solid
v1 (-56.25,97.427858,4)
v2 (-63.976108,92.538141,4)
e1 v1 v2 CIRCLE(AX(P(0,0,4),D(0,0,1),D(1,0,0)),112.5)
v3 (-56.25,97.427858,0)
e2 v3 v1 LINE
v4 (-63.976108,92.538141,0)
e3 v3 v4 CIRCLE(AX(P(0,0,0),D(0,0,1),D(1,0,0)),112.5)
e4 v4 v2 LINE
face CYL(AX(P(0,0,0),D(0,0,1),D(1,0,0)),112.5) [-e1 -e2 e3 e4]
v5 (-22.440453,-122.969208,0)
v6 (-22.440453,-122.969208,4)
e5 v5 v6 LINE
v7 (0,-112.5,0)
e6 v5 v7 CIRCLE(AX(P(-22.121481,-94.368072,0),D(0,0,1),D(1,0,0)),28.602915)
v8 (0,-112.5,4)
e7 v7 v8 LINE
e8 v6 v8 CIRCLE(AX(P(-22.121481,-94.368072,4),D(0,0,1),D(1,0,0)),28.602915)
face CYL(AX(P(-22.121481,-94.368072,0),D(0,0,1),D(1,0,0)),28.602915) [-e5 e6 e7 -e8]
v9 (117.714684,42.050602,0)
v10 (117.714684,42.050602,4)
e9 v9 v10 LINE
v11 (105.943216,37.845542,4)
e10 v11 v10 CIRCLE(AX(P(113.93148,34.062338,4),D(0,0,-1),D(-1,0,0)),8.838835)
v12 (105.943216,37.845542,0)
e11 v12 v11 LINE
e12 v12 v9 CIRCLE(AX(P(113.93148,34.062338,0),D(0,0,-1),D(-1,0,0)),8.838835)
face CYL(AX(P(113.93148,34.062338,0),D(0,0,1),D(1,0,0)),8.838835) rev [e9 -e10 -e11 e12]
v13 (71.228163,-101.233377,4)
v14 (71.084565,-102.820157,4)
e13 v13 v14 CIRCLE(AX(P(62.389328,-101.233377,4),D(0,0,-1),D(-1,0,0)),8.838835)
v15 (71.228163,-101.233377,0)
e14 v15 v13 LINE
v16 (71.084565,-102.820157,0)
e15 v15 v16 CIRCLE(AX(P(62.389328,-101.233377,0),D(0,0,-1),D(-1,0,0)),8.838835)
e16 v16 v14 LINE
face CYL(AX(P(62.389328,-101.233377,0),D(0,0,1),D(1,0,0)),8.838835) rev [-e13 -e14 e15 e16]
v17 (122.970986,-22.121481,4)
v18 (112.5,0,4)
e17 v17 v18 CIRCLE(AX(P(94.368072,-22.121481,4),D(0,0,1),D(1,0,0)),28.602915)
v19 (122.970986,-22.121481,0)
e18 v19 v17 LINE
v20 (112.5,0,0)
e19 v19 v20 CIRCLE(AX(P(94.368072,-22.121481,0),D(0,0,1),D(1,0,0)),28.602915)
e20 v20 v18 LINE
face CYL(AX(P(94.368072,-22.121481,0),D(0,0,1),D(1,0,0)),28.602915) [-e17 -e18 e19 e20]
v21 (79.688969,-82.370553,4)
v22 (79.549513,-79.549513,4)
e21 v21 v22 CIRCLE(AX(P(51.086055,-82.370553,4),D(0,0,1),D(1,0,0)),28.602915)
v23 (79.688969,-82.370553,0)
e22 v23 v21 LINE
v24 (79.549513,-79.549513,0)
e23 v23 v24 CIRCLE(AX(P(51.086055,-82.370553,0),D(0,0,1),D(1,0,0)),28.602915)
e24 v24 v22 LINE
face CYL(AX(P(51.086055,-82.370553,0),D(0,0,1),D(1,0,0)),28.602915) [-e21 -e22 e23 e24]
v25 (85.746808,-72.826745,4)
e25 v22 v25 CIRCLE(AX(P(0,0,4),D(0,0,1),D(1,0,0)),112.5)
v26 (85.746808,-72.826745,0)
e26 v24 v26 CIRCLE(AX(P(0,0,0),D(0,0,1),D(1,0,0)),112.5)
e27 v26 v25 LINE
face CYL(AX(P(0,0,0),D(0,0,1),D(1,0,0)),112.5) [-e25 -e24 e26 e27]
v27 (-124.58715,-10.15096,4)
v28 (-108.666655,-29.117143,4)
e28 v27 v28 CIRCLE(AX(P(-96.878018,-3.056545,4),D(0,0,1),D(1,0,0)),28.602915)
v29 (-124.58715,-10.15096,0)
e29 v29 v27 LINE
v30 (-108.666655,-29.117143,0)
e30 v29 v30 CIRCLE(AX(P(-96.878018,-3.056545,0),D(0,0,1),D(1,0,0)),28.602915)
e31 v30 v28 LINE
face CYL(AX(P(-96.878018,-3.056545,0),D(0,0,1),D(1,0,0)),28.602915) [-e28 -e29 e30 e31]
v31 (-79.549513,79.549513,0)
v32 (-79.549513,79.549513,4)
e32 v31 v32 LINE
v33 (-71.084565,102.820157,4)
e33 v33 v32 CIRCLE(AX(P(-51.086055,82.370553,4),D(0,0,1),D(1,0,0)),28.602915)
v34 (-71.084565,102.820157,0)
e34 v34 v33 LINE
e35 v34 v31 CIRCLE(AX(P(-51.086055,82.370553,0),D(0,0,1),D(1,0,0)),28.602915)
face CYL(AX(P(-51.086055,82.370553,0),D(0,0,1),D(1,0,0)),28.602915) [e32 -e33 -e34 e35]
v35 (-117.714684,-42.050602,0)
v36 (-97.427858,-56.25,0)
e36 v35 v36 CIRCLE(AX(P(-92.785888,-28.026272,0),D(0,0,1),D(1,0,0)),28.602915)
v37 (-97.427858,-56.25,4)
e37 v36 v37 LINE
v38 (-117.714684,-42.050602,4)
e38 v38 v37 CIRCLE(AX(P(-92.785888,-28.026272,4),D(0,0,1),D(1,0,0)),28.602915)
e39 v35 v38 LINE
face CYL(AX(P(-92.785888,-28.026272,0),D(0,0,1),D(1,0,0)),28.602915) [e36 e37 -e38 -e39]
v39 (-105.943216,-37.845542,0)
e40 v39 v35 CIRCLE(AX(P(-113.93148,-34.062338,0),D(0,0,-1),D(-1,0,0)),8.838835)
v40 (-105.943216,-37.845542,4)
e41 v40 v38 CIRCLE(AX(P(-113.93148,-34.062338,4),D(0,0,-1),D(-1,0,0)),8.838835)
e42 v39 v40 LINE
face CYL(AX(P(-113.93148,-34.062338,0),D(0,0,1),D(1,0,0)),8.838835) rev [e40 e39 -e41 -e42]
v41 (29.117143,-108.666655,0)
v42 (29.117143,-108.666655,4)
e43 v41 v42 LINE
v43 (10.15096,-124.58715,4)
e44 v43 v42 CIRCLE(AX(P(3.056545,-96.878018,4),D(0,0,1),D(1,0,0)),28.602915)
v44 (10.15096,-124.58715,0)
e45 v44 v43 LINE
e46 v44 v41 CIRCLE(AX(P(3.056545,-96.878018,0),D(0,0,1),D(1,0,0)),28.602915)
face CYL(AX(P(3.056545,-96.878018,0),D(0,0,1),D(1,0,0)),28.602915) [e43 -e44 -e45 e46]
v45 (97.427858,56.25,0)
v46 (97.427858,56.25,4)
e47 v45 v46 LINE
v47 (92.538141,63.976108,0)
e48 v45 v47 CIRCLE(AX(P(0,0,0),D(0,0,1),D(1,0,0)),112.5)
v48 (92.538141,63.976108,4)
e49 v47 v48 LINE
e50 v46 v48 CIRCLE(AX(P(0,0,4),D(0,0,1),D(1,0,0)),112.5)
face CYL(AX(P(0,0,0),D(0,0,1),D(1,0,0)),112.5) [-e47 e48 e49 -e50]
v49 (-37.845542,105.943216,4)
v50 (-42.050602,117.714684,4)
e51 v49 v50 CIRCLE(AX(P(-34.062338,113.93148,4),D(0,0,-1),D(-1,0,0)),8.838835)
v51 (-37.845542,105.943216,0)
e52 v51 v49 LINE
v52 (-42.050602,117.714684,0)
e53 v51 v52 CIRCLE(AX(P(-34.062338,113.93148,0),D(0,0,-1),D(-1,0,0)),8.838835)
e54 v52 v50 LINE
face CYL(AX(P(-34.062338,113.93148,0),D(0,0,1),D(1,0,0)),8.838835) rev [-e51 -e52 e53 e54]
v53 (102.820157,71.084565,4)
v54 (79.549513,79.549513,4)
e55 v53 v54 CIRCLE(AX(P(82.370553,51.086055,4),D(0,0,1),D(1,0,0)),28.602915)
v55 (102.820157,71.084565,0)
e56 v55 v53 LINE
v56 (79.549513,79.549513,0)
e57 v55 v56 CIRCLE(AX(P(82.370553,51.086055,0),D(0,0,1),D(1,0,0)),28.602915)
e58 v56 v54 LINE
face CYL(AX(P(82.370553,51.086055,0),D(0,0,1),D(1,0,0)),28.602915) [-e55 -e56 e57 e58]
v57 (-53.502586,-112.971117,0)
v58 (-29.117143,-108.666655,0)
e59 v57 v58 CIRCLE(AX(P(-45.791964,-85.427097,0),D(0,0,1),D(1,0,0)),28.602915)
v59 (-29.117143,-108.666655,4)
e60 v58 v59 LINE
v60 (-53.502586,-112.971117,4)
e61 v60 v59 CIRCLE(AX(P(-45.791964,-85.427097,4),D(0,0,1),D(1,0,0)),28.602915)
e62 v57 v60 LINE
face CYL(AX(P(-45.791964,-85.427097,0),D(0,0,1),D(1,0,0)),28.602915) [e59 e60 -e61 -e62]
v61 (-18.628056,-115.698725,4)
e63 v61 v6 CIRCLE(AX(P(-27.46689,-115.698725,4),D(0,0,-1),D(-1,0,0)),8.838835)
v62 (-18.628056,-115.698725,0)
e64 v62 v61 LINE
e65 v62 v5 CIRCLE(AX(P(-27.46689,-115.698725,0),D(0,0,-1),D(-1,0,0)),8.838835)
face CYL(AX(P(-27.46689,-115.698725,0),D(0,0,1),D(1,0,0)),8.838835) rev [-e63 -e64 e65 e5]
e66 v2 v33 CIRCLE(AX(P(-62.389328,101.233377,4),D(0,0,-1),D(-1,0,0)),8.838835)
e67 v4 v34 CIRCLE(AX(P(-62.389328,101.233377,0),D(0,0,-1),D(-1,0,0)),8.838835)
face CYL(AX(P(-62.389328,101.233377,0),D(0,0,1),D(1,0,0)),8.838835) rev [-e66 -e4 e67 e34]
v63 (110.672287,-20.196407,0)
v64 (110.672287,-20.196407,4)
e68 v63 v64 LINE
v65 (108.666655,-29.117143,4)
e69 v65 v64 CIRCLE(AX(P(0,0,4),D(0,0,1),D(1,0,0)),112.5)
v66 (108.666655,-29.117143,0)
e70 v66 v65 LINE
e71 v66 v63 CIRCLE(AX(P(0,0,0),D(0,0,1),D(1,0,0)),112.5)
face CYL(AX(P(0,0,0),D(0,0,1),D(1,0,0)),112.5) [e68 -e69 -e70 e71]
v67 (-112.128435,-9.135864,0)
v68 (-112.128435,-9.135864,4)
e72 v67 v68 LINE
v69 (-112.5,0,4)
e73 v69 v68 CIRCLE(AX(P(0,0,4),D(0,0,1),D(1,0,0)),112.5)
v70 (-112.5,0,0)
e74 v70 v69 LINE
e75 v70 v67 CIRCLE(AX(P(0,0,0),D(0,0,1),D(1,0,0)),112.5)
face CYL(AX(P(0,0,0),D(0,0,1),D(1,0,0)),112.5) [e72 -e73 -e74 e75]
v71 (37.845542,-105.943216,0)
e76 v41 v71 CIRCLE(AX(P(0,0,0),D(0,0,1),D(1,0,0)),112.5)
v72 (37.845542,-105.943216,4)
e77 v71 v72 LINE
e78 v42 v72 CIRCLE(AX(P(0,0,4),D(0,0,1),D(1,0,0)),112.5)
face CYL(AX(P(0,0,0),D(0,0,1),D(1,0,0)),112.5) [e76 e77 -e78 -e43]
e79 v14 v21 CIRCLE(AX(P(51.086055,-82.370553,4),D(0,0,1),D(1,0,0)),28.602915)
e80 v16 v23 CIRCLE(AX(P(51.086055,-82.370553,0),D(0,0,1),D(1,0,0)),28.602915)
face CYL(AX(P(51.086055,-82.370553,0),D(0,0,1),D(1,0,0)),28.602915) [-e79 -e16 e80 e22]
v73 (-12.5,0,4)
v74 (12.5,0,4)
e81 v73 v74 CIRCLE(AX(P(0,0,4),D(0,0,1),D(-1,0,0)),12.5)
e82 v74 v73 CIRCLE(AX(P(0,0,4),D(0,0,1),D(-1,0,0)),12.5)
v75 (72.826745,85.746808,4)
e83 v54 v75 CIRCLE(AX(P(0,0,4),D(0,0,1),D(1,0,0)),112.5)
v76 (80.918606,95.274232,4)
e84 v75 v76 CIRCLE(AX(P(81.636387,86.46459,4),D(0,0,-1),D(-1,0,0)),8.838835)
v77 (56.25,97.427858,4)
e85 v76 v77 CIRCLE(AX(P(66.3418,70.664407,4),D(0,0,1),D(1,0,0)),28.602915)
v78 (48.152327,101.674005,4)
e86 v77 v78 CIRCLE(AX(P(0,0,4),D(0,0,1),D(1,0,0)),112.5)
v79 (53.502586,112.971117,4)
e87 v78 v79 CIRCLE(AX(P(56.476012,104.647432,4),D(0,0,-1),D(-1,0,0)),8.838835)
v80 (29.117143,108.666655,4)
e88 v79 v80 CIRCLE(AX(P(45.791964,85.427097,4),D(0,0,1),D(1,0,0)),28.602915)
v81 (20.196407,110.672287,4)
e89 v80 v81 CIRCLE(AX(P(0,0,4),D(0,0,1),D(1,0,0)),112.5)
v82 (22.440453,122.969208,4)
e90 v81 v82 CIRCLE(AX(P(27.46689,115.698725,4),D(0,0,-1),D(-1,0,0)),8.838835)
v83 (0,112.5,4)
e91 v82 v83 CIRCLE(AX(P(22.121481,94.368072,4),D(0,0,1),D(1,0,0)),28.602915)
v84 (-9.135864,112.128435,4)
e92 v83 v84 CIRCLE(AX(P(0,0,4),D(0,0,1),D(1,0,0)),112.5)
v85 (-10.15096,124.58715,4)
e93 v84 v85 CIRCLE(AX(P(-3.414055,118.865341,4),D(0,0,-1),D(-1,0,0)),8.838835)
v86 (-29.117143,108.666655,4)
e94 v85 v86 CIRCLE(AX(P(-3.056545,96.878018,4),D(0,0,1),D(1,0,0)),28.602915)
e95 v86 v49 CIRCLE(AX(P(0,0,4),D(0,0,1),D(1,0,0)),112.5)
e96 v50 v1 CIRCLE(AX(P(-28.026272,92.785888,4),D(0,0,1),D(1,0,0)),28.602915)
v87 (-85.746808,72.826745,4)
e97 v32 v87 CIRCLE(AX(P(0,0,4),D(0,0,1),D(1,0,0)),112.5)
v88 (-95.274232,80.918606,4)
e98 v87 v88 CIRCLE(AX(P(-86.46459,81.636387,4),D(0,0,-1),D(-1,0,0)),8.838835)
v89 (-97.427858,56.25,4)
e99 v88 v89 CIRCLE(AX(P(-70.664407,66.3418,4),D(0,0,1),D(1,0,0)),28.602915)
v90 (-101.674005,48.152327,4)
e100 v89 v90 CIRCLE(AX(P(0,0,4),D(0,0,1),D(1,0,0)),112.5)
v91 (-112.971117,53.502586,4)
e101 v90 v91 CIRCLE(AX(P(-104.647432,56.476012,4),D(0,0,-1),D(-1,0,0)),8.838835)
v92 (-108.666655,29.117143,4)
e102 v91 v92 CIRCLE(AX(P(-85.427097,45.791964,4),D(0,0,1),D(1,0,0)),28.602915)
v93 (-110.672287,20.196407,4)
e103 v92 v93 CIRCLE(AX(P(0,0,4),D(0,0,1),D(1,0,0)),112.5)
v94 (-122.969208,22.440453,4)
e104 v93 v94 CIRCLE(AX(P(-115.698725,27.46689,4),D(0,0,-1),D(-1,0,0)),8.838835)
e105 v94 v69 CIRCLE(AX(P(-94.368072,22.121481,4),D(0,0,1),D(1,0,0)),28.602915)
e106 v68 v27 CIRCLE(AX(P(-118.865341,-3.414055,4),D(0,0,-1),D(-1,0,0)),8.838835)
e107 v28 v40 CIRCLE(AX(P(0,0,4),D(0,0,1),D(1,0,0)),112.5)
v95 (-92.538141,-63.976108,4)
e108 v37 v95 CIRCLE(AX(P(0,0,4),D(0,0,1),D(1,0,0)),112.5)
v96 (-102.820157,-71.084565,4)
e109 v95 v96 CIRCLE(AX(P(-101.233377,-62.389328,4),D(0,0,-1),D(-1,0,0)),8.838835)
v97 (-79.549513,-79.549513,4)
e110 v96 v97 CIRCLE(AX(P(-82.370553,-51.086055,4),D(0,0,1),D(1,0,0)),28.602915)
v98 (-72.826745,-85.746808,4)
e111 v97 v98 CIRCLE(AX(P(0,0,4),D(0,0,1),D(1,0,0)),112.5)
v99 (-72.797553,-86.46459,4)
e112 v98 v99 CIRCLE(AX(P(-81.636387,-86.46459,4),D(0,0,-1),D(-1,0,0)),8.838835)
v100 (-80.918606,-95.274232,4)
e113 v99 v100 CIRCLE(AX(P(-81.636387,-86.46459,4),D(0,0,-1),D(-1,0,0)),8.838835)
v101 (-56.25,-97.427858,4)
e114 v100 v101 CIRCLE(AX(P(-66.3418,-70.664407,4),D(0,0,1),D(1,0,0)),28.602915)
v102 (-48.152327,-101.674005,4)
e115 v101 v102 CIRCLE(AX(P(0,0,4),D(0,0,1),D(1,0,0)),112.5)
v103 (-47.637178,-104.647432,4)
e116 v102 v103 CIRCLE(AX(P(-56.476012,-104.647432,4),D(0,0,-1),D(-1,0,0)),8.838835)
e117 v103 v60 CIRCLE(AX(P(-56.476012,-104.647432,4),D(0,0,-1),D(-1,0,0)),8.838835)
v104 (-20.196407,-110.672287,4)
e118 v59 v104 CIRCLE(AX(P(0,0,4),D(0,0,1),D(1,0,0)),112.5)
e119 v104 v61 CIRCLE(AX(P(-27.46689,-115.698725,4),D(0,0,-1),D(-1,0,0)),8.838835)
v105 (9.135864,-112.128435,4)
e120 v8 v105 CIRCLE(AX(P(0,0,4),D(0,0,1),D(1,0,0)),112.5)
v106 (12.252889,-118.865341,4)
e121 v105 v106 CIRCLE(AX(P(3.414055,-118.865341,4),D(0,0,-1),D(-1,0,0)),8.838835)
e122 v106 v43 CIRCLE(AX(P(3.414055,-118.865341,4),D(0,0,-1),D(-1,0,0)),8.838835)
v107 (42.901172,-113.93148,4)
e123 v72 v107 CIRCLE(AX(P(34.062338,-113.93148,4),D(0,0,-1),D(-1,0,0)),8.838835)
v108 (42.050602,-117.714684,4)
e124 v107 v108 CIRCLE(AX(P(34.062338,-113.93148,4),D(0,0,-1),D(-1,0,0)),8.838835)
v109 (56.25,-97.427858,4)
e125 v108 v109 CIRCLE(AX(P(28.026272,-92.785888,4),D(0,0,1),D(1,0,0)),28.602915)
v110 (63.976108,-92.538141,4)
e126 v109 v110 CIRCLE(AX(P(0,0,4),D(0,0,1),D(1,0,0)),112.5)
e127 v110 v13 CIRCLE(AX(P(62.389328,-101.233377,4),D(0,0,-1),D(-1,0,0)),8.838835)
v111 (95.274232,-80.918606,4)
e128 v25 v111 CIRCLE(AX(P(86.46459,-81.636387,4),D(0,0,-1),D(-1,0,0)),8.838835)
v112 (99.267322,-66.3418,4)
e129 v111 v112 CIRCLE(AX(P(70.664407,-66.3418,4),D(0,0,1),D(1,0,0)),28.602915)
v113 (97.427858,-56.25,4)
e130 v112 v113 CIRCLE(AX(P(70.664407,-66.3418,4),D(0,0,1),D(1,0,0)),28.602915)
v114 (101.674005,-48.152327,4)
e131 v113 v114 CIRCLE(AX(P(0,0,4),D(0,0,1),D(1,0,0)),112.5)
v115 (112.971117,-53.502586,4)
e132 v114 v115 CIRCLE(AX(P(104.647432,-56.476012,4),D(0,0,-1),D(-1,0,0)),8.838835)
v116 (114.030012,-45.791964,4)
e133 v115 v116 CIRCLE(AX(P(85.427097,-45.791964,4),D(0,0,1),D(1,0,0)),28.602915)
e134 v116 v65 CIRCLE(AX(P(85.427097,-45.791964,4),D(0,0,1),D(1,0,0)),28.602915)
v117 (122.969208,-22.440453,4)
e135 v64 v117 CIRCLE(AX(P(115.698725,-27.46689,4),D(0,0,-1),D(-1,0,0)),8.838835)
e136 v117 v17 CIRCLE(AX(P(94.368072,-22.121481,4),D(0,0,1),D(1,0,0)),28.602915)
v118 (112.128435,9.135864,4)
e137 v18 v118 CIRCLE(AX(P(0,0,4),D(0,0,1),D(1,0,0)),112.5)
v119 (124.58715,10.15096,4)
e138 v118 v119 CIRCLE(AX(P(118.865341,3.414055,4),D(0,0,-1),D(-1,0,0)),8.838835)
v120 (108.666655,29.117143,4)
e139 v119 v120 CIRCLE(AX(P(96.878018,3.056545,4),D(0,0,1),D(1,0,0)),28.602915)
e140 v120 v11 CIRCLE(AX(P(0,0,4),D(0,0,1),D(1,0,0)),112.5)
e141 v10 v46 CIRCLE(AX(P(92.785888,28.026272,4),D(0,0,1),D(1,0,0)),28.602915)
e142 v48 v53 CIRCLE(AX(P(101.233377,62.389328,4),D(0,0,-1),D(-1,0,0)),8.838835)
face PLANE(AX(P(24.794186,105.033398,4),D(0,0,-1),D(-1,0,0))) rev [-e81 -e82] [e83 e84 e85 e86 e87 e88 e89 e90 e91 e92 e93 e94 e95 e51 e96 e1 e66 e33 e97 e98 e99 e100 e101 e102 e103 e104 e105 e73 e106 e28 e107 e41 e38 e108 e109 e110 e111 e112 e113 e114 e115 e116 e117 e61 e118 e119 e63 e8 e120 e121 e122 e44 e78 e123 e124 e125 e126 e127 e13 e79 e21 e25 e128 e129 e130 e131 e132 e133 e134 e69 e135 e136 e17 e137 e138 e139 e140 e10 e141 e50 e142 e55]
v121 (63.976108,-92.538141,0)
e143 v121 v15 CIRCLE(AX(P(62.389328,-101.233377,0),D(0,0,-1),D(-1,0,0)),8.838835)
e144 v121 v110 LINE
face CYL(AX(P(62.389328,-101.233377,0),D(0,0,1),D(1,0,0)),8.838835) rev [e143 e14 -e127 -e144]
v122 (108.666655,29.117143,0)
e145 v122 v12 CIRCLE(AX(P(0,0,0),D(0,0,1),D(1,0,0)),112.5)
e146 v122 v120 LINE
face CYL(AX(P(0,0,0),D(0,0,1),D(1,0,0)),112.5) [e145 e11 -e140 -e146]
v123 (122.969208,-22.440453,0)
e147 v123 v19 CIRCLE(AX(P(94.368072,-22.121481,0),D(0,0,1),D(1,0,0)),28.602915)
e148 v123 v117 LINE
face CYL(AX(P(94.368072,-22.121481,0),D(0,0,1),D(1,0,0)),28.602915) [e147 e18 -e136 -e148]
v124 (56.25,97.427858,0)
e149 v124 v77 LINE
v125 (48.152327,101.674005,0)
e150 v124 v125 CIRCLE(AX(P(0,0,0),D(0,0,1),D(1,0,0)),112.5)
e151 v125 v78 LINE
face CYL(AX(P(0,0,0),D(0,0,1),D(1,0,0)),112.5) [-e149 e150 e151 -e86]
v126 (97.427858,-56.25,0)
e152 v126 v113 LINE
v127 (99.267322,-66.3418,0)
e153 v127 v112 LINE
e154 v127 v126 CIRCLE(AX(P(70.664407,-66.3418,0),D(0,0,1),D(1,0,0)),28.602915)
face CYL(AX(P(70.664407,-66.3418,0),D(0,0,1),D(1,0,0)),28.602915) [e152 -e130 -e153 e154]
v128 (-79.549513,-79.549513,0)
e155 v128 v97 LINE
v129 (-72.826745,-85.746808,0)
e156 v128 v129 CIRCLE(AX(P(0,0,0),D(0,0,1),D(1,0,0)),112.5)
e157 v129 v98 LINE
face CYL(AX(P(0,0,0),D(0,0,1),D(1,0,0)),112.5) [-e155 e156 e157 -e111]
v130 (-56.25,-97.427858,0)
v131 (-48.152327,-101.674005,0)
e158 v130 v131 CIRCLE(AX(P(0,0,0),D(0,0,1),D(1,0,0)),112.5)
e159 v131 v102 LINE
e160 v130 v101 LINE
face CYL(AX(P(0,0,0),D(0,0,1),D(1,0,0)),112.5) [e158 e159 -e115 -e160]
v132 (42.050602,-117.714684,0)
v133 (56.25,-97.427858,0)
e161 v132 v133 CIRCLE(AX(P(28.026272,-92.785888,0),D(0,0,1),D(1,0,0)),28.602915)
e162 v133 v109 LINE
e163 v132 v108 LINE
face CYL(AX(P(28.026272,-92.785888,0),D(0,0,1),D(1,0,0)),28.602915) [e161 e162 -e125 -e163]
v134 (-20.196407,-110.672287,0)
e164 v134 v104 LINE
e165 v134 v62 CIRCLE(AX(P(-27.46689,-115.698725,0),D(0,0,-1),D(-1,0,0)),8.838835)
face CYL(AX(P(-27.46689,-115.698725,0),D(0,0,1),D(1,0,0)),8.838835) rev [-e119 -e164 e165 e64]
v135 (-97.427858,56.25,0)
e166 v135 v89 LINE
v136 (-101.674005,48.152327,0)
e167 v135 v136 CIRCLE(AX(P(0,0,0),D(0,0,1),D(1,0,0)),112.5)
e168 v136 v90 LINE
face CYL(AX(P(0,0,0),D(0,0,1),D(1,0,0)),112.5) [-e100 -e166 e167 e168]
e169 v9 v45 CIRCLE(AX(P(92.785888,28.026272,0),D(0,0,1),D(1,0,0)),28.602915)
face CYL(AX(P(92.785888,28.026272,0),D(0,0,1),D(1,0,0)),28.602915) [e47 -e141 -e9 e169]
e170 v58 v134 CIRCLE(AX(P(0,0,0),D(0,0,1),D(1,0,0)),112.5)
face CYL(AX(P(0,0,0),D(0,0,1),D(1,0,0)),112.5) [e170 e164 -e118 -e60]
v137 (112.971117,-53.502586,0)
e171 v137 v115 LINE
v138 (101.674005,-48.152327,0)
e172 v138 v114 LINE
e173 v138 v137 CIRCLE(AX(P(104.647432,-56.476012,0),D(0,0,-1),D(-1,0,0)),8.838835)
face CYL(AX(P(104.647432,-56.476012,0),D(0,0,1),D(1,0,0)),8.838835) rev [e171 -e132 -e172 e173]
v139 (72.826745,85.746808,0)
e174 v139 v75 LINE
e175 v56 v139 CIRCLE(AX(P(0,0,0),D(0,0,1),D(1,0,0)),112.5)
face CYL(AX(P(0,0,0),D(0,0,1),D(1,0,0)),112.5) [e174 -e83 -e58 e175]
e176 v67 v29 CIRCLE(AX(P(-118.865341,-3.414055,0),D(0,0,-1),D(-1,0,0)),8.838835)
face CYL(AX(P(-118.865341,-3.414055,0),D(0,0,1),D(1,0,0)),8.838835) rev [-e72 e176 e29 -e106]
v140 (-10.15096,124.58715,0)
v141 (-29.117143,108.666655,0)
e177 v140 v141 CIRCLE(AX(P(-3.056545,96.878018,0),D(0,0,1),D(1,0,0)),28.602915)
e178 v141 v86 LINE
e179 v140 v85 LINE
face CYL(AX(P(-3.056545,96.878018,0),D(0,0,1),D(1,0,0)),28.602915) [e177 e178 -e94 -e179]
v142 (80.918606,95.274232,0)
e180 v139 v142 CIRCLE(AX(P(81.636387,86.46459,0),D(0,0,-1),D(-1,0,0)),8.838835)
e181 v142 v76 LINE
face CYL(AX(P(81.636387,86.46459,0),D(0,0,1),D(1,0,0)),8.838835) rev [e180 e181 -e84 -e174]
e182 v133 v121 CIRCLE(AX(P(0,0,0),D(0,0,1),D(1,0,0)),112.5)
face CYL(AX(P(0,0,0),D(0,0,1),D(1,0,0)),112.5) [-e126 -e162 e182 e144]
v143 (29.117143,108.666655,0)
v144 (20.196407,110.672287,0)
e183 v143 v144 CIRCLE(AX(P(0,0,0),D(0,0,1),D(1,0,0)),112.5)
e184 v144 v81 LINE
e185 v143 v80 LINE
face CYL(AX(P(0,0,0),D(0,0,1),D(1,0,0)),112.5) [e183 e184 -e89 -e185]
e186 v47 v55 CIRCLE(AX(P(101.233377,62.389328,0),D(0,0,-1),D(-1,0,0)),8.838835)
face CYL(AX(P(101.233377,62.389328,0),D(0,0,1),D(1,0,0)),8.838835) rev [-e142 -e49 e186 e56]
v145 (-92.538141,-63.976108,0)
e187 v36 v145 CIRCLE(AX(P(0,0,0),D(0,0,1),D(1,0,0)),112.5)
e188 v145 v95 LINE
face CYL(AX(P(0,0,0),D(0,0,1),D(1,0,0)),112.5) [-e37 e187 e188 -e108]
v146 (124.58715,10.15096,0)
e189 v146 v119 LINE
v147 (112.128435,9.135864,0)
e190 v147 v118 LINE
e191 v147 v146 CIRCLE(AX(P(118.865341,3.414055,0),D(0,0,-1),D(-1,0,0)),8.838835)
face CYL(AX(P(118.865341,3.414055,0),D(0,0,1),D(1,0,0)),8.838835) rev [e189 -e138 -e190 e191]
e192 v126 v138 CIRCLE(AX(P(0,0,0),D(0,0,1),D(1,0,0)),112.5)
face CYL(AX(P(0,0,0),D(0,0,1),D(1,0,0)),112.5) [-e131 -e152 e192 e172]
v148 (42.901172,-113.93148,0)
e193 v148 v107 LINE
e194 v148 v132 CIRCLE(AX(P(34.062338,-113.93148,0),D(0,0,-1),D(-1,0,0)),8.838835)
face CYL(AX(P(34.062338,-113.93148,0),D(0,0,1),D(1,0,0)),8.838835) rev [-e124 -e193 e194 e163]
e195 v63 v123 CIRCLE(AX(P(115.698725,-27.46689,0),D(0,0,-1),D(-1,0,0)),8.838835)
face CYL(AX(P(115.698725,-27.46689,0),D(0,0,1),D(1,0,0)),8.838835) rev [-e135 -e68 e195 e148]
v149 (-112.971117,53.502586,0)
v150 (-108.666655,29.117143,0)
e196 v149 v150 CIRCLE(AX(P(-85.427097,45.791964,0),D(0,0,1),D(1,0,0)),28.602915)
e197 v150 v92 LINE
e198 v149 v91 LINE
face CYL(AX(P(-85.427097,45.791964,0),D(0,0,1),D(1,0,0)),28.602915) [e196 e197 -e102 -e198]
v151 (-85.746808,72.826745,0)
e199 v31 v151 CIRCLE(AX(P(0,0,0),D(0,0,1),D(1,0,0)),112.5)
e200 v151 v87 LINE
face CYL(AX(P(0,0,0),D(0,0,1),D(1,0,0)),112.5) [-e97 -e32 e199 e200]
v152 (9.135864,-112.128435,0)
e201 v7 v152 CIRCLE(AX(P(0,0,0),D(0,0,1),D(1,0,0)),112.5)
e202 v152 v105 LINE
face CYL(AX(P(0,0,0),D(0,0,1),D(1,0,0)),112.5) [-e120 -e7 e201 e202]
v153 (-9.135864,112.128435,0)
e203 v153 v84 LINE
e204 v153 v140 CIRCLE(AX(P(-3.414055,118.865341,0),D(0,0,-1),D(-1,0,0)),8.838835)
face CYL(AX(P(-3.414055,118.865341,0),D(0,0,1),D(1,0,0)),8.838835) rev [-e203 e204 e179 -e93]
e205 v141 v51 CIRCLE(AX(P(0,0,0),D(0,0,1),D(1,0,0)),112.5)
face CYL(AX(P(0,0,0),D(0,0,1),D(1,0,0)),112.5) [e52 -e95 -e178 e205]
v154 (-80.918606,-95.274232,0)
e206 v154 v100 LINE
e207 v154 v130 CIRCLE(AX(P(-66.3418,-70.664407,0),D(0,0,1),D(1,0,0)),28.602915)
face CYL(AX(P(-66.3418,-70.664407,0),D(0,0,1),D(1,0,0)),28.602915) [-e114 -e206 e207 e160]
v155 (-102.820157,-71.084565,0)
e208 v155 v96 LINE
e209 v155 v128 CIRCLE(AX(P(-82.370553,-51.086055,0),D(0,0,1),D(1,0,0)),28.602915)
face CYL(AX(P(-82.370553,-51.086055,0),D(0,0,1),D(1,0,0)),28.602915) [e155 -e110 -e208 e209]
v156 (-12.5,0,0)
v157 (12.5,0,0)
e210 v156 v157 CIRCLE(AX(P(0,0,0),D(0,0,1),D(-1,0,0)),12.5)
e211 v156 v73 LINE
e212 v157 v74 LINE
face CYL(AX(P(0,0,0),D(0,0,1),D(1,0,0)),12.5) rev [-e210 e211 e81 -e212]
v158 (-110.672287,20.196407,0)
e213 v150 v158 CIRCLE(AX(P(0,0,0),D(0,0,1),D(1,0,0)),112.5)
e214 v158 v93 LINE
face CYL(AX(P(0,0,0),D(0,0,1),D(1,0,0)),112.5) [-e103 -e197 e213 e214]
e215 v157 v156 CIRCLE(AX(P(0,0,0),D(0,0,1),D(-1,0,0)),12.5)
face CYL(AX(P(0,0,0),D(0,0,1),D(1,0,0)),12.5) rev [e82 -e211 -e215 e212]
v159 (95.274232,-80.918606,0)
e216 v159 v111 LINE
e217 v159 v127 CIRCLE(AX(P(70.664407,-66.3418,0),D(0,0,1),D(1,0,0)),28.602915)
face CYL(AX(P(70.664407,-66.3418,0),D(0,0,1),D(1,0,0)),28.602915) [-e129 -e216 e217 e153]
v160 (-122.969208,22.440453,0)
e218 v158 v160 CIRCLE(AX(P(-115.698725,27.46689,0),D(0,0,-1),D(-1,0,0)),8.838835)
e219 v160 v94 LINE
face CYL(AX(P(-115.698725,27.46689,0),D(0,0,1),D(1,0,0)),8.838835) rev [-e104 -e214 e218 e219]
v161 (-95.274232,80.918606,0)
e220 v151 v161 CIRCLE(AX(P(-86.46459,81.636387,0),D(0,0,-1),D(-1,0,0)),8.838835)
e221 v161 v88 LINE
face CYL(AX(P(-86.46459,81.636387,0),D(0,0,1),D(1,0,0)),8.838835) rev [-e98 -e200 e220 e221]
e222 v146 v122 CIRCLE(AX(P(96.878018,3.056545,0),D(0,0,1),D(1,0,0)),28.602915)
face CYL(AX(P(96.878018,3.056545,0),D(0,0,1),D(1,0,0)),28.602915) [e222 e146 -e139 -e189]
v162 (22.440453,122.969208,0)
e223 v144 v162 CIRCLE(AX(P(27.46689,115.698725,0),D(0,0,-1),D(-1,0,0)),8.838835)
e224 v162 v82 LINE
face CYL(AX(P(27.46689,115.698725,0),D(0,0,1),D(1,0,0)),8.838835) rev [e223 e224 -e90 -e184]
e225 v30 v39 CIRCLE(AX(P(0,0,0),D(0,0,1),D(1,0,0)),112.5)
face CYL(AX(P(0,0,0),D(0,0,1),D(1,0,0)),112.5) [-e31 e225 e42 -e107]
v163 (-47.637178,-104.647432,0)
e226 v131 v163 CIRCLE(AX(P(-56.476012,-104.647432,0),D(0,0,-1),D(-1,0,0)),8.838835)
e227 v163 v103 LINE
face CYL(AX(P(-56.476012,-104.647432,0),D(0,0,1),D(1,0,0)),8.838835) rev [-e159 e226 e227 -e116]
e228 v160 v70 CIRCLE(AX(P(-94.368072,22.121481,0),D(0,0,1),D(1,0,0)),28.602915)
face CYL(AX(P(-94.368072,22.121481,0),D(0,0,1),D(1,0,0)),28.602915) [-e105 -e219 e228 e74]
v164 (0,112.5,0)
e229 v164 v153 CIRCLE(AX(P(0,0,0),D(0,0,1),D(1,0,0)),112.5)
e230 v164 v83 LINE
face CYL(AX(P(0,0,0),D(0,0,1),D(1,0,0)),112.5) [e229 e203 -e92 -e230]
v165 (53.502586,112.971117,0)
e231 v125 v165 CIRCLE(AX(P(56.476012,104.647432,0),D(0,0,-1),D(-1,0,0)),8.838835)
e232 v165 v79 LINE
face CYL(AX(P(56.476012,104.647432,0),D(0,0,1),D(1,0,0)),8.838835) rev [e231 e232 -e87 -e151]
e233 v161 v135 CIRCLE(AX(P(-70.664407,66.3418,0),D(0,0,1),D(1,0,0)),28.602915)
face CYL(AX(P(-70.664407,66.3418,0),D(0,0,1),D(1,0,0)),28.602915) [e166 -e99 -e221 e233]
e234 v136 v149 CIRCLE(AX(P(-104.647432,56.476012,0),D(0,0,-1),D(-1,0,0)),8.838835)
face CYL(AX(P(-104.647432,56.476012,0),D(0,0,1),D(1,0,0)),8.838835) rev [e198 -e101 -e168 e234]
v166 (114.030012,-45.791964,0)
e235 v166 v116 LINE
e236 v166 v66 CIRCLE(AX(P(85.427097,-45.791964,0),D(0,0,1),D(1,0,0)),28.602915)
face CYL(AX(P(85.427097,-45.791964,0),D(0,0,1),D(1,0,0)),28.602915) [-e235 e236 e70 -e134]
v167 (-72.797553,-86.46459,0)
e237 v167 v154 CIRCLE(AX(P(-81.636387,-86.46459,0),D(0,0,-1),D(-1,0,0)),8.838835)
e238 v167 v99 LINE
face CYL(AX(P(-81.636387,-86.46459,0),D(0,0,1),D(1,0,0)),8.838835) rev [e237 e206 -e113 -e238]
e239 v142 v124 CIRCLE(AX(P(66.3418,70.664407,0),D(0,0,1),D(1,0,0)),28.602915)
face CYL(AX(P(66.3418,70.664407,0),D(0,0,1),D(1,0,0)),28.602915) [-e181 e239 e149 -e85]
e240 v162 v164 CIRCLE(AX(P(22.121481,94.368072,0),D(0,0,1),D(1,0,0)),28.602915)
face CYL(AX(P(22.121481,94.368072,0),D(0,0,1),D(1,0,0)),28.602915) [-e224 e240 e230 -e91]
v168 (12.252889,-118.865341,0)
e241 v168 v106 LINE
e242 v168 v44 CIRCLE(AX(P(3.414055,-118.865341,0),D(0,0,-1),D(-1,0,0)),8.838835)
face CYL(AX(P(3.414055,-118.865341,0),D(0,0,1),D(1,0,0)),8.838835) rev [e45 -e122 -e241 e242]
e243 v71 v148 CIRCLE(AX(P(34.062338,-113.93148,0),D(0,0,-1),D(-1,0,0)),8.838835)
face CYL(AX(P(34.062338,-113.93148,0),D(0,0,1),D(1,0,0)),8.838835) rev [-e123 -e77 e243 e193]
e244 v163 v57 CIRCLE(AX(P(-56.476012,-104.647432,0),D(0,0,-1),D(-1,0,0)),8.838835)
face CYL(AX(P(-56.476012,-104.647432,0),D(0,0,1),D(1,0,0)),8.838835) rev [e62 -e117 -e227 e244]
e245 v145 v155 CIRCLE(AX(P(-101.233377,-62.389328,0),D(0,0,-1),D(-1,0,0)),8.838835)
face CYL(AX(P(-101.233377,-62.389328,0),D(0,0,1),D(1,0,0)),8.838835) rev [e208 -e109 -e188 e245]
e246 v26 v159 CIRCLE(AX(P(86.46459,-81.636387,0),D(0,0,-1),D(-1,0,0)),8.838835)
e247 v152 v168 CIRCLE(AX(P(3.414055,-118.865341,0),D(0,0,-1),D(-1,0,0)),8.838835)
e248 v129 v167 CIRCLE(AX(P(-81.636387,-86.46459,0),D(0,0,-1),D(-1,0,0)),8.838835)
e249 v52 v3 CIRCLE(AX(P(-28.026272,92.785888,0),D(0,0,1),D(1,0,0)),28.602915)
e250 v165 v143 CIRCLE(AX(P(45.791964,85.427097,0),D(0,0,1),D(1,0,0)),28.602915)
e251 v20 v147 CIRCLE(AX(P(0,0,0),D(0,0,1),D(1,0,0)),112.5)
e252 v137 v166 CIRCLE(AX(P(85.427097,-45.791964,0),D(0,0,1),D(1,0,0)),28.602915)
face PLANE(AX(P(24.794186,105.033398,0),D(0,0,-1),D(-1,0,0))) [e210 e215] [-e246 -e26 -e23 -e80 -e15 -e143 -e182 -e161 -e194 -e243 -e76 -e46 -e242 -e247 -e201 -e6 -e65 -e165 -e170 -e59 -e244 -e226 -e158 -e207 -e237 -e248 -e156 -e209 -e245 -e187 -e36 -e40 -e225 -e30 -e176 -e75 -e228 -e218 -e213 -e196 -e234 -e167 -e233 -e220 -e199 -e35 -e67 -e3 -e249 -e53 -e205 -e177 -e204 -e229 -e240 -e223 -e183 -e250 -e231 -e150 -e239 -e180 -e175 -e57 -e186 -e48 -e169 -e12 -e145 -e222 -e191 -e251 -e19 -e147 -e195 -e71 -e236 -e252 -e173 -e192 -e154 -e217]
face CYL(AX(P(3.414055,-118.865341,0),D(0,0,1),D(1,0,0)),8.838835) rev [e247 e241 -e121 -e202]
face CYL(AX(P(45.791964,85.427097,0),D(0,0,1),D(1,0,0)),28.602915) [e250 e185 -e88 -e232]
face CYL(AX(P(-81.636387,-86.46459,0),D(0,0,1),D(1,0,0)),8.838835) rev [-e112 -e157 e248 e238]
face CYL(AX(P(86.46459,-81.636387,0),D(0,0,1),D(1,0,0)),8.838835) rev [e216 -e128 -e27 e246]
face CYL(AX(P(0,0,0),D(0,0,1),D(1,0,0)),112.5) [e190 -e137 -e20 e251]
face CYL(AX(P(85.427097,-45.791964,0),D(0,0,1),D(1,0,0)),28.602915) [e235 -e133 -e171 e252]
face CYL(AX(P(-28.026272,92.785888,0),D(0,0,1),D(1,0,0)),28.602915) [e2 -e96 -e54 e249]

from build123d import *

# Parameters (mm, degrees)
SKETCH1_R           = 12.5
BOSS_EXTRUDE1_DEPTH = 4


with BuildPart() as part:
    # Sketch1 → Boss-Extrude1 (new body)
    with BuildSketch(Plane.XY.offset(4)):
        with BuildLine():
            ThreePointArc((22.440452668, 122.96920787), (10.028572641, 120.288880116), (0, 112.5))
            ThreePointArc((0, 112.5), (-4.571708495, 112.407070425), (-9.135864155, 112.128435226))
            ThreePointArc((-9.135864155, 112.128435226), (-12.223696531, 118.147559469), (-10.150960173, 124.587150251))
            ThreePointArc((-10.150960173, 124.587150251), (-21.446195774, 118.785721514), (-29.117142574, 108.666655458))
            ThreePointArc((-29.117142574, 108.666655458), (-33.509021935, 107.393647153), (-37.845541667, 105.943215809))
            ThreePointArc((-37.845541667, 105.943215809), (-42.386022695, 110.958053541), (-42.050601852, 117.714684232))
            ThreePointArc((-42.050601852, 117.714684232), (-51.459441387, 109.187512293), (-56.25, 97.427857926))
            ThreePointArc((-56.25, 97.427857926), (-60.162750907, 95.061524305), (-63.976108057, 92.538141314))
            ThreePointArc((-63.976108057, 92.538141314), (-69.659811458, 96.20693963), (-71.084564508, 102.820157016))
            ThreePointArc((-71.084564508, 102.820157016), (-77.965811111, 92.148354551), (-79.549512883, 79.549512883))
            ThreePointArc((-79.549512883, 79.549512883), (-82.716487829, 76.251115672), (-85.746808408, 72.826745416))
            ThreePointArc((-85.746808408, 72.826745416), (-92.186399189, 74.899481774), (-95.274231565, 80.918606017))
            ThreePointArc((-95.274231565, 80.918606017), (-99.158939653, 68.829438728), (-97.427857926, 56.25))
            ThreePointArc((-97.427857926, 56.25), (-99.6332328, 52.244319517), (-101.67400547, 48.152327169))
            ThreePointArc((-101.67400547, 48.152327169), (-108.430636161, 48.487748011), (-112.971117188, 53.502585743))
            ThreePointArc((-112.971117188, 53.502585743), (-113.594550325, 40.819910403), (-108.666655458, 29.117142574))
            ThreePointArc((-108.666655458, 29.117142574), (-109.760137608, 24.677159325), (-110.672287083, 20.196407401))
            ThreePointArc((-110.672287083, 20.196407401), (-117.285504468, 18.771654352), (-122.96920787, 22.440452668))
            ThreePointArc((-122.96920787, 22.440452668), (-120.288880116, 10.028572641), (-112.5, 0))
            ThreePointArc((-112.5, 0), (-112.407070425, -4.571708495), (-112.128435226, -9.135864155))
            ThreePointArc((-112.128435226, -9.135864155), (-118.147559469, -12.223696531), (-124.587150251, -10.150960173))
            ThreePointArc((-124.587150251, -10.150960173), (-118.785721514, -21.446195774), (-108.666655458, -29.117142574))
            ThreePointArc((-108.666655458, -29.117142574), (-107.393647153, -33.509021935), (-105.943215809, -37.845541667))
            ThreePointArc((-105.943215809, -37.845541667), (-110.958053541, -42.386022695), (-117.714684232, -42.050601852))
            ThreePointArc((-117.714684232, -42.050601852), (-109.187512293, -51.459441387), (-97.427857926, -56.25))
            ThreePointArc((-97.427857926, -56.25), (-95.061524305, -60.162750907), (-92.538141314, -63.976108057))
            ThreePointArc((-92.538141314, -63.976108057), (-96.20693963, -69.659811458), (-102.820157016, -71.084564508))
            ThreePointArc((-102.820157016, -71.084564508), (-92.148354551, -77.965811111), (-79.549512883, -79.549512883))
            ThreePointArc((-79.549512883, -79.549512883), (-76.251115672, -82.716487829), (-72.826745416, -85.746808408))
            ThreePointArc((-72.826745416, -85.746808408), (-74.899481774, -92.186399189), (-80.918606017, -95.274231565))
            ThreePointArc((-80.918606017, -95.274231565), (-68.829438728, -99.158939653), (-56.25, -97.427857926))
            ThreePointArc((-56.25, -97.427857926), (-52.244319517, -99.6332328), (-48.152327169, -101.67400547))
            ThreePointArc((-48.152327169, -101.67400547), (-48.487748011, -108.430636161), (-53.502585743, -112.971117188))
            ThreePointArc((-53.502585743, -112.971117188), (-40.819910403, -113.594550325), (-29.117142574, -108.666655458))
            ThreePointArc((-29.117142574, -108.666655458), (-24.677159325, -109.760137608), (-20.196407401, -110.672287083))
            ThreePointArc((-20.196407401, -110.672287083), (-18.771654352, -117.285504468), (-22.440452668, -122.96920787))
            ThreePointArc((-22.440452668, -122.96920787), (-10.028572641, -120.288880116), (0, -112.5))
            ThreePointArc((0, -112.5), (4.571708495, -112.407070425), (9.135864155, -112.128435226))
            ThreePointArc((9.135864155, -112.128435226), (12.223696531, -118.147559469), (10.150960173, -124.587150251))
            ThreePointArc((10.150960173, -124.587150251), (21.446195774, -118.785721514), (29.117142574, -108.666655458))
            ThreePointArc((29.117142574, -108.666655458), (33.509021935, -107.393647153), (37.845541667, -105.943215809))
            ThreePointArc((37.845541667, -105.943215809), (42.386022695, -110.958053541), (42.050601852, -117.714684232))
            ThreePointArc((42.050601852, -117.714684232), (51.459441387, -109.187512293), (56.25, -97.427857926))
            ThreePointArc((56.25, -97.427857926), (60.162750907, -95.061524305), (63.976108057, -92.538141314))
            ThreePointArc((63.976108057, -92.538141314), (69.659811458, -96.20693963), (71.084564508, -102.820157016))
            ThreePointArc((71.084564508, -102.820157016), (77.965811111, -92.148354551), (79.549512883, -79.549512883))
            ThreePointArc((79.549512883, -79.549512883), (82.716487829, -76.251115672), (85.746808408, -72.826745416))
            ThreePointArc((85.746808408, -72.826745416), (92.186399189, -74.899481774), (95.274231565, -80.918606017))
            ThreePointArc((95.274231565, -80.918606017), (99.158939653, -68.829438728), (97.427857926, -56.25))
            ThreePointArc((97.427857926, -56.25), (99.6332328, -52.244319517), (101.67400547, -48.152327169))
            ThreePointArc((101.67400547, -48.152327169), (108.430636161, -48.487748011), (112.971117188, -53.502585743))
            ThreePointArc((112.971117188, -53.502585743), (113.594550325, -40.819910403), (108.666655458, -29.117142574))
            ThreePointArc((108.666655458, -29.117142574), (109.760137608, -24.677159325), (110.672287083, -20.196407401))
            ThreePointArc((110.672287083, -20.196407401), (117.285504468, -18.771654352), (122.96920787, -22.440452668))
            ThreePointArc((122.96920787, -22.440452668), (120.288880116, -10.028572641), (112.5, 0))
            ThreePointArc((112.5, 0), (112.407070425, 4.571708495), (112.128435226, 9.135864155))
            ThreePointArc((112.128435226, 9.135864155), (118.147559469, 12.223696531), (124.587150251, 10.150960173))
            ThreePointArc((124.587150251, 10.150960173), (118.785721514, 21.446195774), (108.666655458, 29.117142574))
            ThreePointArc((108.666655458, 29.117142574), (107.393647153, 33.509021935), (105.943215809, 37.845541667))
            ThreePointArc((105.943215809, 37.845541667), (110.958053541, 42.386022695), (117.714684232, 42.050601852))
            ThreePointArc((117.714684232, 42.050601852), (109.187512293, 51.459441387), (97.427857926, 56.25))
            ThreePointArc((97.427857926, 56.25), (95.061524305, 60.162750907), (92.538141314, 63.976108057))
            ThreePointArc((92.538141314, 63.976108057), (96.20693963, 69.659811458), (102.820157016, 71.084564508))
            ThreePointArc((102.820157016, 71.084564508), (92.148354551, 77.965811111), (79.549512883, 79.549512883))
            ThreePointArc((79.549512883, 79.549512883), (76.251115672, 82.716487829), (72.826745416, 85.746808408))
            ThreePointArc((72.826745416, 85.746808408), (74.899481774, 92.186399189), (80.918606017, 95.274231565))
            ThreePointArc((80.918606017, 95.274231565), (68.829438728, 99.158939653), (56.25, 97.427857926))
            ThreePointArc((56.25, 97.427857926), (52.244319517, 99.6332328), (48.152327169, 101.67400547))
            ThreePointArc((48.152327169, 101.67400547), (48.487748011, 108.430636161), (53.502585743, 112.971117188))
            ThreePointArc((53.502585743, 112.971117188), (40.819910403, 113.594550325), (29.117142574, 108.666655458))
            ThreePointArc((29.117142574, 108.666655458), (24.677159325, 109.760137608), (20.196407401, 110.672287083))
            ThreePointArc((20.196407401, 110.672287083), (18.771654352, 117.285504468), (22.440452668, 122.96920787))
        make_face()
        with Locations(Location((0, 0, 0), (0, 0, 180))):
            Circle(SKETCH1_R, mode=Mode.SUBTRACT)
    extrude(amount=-BOSS_EXTRUDE1_DEPTH)


solid = part.part
